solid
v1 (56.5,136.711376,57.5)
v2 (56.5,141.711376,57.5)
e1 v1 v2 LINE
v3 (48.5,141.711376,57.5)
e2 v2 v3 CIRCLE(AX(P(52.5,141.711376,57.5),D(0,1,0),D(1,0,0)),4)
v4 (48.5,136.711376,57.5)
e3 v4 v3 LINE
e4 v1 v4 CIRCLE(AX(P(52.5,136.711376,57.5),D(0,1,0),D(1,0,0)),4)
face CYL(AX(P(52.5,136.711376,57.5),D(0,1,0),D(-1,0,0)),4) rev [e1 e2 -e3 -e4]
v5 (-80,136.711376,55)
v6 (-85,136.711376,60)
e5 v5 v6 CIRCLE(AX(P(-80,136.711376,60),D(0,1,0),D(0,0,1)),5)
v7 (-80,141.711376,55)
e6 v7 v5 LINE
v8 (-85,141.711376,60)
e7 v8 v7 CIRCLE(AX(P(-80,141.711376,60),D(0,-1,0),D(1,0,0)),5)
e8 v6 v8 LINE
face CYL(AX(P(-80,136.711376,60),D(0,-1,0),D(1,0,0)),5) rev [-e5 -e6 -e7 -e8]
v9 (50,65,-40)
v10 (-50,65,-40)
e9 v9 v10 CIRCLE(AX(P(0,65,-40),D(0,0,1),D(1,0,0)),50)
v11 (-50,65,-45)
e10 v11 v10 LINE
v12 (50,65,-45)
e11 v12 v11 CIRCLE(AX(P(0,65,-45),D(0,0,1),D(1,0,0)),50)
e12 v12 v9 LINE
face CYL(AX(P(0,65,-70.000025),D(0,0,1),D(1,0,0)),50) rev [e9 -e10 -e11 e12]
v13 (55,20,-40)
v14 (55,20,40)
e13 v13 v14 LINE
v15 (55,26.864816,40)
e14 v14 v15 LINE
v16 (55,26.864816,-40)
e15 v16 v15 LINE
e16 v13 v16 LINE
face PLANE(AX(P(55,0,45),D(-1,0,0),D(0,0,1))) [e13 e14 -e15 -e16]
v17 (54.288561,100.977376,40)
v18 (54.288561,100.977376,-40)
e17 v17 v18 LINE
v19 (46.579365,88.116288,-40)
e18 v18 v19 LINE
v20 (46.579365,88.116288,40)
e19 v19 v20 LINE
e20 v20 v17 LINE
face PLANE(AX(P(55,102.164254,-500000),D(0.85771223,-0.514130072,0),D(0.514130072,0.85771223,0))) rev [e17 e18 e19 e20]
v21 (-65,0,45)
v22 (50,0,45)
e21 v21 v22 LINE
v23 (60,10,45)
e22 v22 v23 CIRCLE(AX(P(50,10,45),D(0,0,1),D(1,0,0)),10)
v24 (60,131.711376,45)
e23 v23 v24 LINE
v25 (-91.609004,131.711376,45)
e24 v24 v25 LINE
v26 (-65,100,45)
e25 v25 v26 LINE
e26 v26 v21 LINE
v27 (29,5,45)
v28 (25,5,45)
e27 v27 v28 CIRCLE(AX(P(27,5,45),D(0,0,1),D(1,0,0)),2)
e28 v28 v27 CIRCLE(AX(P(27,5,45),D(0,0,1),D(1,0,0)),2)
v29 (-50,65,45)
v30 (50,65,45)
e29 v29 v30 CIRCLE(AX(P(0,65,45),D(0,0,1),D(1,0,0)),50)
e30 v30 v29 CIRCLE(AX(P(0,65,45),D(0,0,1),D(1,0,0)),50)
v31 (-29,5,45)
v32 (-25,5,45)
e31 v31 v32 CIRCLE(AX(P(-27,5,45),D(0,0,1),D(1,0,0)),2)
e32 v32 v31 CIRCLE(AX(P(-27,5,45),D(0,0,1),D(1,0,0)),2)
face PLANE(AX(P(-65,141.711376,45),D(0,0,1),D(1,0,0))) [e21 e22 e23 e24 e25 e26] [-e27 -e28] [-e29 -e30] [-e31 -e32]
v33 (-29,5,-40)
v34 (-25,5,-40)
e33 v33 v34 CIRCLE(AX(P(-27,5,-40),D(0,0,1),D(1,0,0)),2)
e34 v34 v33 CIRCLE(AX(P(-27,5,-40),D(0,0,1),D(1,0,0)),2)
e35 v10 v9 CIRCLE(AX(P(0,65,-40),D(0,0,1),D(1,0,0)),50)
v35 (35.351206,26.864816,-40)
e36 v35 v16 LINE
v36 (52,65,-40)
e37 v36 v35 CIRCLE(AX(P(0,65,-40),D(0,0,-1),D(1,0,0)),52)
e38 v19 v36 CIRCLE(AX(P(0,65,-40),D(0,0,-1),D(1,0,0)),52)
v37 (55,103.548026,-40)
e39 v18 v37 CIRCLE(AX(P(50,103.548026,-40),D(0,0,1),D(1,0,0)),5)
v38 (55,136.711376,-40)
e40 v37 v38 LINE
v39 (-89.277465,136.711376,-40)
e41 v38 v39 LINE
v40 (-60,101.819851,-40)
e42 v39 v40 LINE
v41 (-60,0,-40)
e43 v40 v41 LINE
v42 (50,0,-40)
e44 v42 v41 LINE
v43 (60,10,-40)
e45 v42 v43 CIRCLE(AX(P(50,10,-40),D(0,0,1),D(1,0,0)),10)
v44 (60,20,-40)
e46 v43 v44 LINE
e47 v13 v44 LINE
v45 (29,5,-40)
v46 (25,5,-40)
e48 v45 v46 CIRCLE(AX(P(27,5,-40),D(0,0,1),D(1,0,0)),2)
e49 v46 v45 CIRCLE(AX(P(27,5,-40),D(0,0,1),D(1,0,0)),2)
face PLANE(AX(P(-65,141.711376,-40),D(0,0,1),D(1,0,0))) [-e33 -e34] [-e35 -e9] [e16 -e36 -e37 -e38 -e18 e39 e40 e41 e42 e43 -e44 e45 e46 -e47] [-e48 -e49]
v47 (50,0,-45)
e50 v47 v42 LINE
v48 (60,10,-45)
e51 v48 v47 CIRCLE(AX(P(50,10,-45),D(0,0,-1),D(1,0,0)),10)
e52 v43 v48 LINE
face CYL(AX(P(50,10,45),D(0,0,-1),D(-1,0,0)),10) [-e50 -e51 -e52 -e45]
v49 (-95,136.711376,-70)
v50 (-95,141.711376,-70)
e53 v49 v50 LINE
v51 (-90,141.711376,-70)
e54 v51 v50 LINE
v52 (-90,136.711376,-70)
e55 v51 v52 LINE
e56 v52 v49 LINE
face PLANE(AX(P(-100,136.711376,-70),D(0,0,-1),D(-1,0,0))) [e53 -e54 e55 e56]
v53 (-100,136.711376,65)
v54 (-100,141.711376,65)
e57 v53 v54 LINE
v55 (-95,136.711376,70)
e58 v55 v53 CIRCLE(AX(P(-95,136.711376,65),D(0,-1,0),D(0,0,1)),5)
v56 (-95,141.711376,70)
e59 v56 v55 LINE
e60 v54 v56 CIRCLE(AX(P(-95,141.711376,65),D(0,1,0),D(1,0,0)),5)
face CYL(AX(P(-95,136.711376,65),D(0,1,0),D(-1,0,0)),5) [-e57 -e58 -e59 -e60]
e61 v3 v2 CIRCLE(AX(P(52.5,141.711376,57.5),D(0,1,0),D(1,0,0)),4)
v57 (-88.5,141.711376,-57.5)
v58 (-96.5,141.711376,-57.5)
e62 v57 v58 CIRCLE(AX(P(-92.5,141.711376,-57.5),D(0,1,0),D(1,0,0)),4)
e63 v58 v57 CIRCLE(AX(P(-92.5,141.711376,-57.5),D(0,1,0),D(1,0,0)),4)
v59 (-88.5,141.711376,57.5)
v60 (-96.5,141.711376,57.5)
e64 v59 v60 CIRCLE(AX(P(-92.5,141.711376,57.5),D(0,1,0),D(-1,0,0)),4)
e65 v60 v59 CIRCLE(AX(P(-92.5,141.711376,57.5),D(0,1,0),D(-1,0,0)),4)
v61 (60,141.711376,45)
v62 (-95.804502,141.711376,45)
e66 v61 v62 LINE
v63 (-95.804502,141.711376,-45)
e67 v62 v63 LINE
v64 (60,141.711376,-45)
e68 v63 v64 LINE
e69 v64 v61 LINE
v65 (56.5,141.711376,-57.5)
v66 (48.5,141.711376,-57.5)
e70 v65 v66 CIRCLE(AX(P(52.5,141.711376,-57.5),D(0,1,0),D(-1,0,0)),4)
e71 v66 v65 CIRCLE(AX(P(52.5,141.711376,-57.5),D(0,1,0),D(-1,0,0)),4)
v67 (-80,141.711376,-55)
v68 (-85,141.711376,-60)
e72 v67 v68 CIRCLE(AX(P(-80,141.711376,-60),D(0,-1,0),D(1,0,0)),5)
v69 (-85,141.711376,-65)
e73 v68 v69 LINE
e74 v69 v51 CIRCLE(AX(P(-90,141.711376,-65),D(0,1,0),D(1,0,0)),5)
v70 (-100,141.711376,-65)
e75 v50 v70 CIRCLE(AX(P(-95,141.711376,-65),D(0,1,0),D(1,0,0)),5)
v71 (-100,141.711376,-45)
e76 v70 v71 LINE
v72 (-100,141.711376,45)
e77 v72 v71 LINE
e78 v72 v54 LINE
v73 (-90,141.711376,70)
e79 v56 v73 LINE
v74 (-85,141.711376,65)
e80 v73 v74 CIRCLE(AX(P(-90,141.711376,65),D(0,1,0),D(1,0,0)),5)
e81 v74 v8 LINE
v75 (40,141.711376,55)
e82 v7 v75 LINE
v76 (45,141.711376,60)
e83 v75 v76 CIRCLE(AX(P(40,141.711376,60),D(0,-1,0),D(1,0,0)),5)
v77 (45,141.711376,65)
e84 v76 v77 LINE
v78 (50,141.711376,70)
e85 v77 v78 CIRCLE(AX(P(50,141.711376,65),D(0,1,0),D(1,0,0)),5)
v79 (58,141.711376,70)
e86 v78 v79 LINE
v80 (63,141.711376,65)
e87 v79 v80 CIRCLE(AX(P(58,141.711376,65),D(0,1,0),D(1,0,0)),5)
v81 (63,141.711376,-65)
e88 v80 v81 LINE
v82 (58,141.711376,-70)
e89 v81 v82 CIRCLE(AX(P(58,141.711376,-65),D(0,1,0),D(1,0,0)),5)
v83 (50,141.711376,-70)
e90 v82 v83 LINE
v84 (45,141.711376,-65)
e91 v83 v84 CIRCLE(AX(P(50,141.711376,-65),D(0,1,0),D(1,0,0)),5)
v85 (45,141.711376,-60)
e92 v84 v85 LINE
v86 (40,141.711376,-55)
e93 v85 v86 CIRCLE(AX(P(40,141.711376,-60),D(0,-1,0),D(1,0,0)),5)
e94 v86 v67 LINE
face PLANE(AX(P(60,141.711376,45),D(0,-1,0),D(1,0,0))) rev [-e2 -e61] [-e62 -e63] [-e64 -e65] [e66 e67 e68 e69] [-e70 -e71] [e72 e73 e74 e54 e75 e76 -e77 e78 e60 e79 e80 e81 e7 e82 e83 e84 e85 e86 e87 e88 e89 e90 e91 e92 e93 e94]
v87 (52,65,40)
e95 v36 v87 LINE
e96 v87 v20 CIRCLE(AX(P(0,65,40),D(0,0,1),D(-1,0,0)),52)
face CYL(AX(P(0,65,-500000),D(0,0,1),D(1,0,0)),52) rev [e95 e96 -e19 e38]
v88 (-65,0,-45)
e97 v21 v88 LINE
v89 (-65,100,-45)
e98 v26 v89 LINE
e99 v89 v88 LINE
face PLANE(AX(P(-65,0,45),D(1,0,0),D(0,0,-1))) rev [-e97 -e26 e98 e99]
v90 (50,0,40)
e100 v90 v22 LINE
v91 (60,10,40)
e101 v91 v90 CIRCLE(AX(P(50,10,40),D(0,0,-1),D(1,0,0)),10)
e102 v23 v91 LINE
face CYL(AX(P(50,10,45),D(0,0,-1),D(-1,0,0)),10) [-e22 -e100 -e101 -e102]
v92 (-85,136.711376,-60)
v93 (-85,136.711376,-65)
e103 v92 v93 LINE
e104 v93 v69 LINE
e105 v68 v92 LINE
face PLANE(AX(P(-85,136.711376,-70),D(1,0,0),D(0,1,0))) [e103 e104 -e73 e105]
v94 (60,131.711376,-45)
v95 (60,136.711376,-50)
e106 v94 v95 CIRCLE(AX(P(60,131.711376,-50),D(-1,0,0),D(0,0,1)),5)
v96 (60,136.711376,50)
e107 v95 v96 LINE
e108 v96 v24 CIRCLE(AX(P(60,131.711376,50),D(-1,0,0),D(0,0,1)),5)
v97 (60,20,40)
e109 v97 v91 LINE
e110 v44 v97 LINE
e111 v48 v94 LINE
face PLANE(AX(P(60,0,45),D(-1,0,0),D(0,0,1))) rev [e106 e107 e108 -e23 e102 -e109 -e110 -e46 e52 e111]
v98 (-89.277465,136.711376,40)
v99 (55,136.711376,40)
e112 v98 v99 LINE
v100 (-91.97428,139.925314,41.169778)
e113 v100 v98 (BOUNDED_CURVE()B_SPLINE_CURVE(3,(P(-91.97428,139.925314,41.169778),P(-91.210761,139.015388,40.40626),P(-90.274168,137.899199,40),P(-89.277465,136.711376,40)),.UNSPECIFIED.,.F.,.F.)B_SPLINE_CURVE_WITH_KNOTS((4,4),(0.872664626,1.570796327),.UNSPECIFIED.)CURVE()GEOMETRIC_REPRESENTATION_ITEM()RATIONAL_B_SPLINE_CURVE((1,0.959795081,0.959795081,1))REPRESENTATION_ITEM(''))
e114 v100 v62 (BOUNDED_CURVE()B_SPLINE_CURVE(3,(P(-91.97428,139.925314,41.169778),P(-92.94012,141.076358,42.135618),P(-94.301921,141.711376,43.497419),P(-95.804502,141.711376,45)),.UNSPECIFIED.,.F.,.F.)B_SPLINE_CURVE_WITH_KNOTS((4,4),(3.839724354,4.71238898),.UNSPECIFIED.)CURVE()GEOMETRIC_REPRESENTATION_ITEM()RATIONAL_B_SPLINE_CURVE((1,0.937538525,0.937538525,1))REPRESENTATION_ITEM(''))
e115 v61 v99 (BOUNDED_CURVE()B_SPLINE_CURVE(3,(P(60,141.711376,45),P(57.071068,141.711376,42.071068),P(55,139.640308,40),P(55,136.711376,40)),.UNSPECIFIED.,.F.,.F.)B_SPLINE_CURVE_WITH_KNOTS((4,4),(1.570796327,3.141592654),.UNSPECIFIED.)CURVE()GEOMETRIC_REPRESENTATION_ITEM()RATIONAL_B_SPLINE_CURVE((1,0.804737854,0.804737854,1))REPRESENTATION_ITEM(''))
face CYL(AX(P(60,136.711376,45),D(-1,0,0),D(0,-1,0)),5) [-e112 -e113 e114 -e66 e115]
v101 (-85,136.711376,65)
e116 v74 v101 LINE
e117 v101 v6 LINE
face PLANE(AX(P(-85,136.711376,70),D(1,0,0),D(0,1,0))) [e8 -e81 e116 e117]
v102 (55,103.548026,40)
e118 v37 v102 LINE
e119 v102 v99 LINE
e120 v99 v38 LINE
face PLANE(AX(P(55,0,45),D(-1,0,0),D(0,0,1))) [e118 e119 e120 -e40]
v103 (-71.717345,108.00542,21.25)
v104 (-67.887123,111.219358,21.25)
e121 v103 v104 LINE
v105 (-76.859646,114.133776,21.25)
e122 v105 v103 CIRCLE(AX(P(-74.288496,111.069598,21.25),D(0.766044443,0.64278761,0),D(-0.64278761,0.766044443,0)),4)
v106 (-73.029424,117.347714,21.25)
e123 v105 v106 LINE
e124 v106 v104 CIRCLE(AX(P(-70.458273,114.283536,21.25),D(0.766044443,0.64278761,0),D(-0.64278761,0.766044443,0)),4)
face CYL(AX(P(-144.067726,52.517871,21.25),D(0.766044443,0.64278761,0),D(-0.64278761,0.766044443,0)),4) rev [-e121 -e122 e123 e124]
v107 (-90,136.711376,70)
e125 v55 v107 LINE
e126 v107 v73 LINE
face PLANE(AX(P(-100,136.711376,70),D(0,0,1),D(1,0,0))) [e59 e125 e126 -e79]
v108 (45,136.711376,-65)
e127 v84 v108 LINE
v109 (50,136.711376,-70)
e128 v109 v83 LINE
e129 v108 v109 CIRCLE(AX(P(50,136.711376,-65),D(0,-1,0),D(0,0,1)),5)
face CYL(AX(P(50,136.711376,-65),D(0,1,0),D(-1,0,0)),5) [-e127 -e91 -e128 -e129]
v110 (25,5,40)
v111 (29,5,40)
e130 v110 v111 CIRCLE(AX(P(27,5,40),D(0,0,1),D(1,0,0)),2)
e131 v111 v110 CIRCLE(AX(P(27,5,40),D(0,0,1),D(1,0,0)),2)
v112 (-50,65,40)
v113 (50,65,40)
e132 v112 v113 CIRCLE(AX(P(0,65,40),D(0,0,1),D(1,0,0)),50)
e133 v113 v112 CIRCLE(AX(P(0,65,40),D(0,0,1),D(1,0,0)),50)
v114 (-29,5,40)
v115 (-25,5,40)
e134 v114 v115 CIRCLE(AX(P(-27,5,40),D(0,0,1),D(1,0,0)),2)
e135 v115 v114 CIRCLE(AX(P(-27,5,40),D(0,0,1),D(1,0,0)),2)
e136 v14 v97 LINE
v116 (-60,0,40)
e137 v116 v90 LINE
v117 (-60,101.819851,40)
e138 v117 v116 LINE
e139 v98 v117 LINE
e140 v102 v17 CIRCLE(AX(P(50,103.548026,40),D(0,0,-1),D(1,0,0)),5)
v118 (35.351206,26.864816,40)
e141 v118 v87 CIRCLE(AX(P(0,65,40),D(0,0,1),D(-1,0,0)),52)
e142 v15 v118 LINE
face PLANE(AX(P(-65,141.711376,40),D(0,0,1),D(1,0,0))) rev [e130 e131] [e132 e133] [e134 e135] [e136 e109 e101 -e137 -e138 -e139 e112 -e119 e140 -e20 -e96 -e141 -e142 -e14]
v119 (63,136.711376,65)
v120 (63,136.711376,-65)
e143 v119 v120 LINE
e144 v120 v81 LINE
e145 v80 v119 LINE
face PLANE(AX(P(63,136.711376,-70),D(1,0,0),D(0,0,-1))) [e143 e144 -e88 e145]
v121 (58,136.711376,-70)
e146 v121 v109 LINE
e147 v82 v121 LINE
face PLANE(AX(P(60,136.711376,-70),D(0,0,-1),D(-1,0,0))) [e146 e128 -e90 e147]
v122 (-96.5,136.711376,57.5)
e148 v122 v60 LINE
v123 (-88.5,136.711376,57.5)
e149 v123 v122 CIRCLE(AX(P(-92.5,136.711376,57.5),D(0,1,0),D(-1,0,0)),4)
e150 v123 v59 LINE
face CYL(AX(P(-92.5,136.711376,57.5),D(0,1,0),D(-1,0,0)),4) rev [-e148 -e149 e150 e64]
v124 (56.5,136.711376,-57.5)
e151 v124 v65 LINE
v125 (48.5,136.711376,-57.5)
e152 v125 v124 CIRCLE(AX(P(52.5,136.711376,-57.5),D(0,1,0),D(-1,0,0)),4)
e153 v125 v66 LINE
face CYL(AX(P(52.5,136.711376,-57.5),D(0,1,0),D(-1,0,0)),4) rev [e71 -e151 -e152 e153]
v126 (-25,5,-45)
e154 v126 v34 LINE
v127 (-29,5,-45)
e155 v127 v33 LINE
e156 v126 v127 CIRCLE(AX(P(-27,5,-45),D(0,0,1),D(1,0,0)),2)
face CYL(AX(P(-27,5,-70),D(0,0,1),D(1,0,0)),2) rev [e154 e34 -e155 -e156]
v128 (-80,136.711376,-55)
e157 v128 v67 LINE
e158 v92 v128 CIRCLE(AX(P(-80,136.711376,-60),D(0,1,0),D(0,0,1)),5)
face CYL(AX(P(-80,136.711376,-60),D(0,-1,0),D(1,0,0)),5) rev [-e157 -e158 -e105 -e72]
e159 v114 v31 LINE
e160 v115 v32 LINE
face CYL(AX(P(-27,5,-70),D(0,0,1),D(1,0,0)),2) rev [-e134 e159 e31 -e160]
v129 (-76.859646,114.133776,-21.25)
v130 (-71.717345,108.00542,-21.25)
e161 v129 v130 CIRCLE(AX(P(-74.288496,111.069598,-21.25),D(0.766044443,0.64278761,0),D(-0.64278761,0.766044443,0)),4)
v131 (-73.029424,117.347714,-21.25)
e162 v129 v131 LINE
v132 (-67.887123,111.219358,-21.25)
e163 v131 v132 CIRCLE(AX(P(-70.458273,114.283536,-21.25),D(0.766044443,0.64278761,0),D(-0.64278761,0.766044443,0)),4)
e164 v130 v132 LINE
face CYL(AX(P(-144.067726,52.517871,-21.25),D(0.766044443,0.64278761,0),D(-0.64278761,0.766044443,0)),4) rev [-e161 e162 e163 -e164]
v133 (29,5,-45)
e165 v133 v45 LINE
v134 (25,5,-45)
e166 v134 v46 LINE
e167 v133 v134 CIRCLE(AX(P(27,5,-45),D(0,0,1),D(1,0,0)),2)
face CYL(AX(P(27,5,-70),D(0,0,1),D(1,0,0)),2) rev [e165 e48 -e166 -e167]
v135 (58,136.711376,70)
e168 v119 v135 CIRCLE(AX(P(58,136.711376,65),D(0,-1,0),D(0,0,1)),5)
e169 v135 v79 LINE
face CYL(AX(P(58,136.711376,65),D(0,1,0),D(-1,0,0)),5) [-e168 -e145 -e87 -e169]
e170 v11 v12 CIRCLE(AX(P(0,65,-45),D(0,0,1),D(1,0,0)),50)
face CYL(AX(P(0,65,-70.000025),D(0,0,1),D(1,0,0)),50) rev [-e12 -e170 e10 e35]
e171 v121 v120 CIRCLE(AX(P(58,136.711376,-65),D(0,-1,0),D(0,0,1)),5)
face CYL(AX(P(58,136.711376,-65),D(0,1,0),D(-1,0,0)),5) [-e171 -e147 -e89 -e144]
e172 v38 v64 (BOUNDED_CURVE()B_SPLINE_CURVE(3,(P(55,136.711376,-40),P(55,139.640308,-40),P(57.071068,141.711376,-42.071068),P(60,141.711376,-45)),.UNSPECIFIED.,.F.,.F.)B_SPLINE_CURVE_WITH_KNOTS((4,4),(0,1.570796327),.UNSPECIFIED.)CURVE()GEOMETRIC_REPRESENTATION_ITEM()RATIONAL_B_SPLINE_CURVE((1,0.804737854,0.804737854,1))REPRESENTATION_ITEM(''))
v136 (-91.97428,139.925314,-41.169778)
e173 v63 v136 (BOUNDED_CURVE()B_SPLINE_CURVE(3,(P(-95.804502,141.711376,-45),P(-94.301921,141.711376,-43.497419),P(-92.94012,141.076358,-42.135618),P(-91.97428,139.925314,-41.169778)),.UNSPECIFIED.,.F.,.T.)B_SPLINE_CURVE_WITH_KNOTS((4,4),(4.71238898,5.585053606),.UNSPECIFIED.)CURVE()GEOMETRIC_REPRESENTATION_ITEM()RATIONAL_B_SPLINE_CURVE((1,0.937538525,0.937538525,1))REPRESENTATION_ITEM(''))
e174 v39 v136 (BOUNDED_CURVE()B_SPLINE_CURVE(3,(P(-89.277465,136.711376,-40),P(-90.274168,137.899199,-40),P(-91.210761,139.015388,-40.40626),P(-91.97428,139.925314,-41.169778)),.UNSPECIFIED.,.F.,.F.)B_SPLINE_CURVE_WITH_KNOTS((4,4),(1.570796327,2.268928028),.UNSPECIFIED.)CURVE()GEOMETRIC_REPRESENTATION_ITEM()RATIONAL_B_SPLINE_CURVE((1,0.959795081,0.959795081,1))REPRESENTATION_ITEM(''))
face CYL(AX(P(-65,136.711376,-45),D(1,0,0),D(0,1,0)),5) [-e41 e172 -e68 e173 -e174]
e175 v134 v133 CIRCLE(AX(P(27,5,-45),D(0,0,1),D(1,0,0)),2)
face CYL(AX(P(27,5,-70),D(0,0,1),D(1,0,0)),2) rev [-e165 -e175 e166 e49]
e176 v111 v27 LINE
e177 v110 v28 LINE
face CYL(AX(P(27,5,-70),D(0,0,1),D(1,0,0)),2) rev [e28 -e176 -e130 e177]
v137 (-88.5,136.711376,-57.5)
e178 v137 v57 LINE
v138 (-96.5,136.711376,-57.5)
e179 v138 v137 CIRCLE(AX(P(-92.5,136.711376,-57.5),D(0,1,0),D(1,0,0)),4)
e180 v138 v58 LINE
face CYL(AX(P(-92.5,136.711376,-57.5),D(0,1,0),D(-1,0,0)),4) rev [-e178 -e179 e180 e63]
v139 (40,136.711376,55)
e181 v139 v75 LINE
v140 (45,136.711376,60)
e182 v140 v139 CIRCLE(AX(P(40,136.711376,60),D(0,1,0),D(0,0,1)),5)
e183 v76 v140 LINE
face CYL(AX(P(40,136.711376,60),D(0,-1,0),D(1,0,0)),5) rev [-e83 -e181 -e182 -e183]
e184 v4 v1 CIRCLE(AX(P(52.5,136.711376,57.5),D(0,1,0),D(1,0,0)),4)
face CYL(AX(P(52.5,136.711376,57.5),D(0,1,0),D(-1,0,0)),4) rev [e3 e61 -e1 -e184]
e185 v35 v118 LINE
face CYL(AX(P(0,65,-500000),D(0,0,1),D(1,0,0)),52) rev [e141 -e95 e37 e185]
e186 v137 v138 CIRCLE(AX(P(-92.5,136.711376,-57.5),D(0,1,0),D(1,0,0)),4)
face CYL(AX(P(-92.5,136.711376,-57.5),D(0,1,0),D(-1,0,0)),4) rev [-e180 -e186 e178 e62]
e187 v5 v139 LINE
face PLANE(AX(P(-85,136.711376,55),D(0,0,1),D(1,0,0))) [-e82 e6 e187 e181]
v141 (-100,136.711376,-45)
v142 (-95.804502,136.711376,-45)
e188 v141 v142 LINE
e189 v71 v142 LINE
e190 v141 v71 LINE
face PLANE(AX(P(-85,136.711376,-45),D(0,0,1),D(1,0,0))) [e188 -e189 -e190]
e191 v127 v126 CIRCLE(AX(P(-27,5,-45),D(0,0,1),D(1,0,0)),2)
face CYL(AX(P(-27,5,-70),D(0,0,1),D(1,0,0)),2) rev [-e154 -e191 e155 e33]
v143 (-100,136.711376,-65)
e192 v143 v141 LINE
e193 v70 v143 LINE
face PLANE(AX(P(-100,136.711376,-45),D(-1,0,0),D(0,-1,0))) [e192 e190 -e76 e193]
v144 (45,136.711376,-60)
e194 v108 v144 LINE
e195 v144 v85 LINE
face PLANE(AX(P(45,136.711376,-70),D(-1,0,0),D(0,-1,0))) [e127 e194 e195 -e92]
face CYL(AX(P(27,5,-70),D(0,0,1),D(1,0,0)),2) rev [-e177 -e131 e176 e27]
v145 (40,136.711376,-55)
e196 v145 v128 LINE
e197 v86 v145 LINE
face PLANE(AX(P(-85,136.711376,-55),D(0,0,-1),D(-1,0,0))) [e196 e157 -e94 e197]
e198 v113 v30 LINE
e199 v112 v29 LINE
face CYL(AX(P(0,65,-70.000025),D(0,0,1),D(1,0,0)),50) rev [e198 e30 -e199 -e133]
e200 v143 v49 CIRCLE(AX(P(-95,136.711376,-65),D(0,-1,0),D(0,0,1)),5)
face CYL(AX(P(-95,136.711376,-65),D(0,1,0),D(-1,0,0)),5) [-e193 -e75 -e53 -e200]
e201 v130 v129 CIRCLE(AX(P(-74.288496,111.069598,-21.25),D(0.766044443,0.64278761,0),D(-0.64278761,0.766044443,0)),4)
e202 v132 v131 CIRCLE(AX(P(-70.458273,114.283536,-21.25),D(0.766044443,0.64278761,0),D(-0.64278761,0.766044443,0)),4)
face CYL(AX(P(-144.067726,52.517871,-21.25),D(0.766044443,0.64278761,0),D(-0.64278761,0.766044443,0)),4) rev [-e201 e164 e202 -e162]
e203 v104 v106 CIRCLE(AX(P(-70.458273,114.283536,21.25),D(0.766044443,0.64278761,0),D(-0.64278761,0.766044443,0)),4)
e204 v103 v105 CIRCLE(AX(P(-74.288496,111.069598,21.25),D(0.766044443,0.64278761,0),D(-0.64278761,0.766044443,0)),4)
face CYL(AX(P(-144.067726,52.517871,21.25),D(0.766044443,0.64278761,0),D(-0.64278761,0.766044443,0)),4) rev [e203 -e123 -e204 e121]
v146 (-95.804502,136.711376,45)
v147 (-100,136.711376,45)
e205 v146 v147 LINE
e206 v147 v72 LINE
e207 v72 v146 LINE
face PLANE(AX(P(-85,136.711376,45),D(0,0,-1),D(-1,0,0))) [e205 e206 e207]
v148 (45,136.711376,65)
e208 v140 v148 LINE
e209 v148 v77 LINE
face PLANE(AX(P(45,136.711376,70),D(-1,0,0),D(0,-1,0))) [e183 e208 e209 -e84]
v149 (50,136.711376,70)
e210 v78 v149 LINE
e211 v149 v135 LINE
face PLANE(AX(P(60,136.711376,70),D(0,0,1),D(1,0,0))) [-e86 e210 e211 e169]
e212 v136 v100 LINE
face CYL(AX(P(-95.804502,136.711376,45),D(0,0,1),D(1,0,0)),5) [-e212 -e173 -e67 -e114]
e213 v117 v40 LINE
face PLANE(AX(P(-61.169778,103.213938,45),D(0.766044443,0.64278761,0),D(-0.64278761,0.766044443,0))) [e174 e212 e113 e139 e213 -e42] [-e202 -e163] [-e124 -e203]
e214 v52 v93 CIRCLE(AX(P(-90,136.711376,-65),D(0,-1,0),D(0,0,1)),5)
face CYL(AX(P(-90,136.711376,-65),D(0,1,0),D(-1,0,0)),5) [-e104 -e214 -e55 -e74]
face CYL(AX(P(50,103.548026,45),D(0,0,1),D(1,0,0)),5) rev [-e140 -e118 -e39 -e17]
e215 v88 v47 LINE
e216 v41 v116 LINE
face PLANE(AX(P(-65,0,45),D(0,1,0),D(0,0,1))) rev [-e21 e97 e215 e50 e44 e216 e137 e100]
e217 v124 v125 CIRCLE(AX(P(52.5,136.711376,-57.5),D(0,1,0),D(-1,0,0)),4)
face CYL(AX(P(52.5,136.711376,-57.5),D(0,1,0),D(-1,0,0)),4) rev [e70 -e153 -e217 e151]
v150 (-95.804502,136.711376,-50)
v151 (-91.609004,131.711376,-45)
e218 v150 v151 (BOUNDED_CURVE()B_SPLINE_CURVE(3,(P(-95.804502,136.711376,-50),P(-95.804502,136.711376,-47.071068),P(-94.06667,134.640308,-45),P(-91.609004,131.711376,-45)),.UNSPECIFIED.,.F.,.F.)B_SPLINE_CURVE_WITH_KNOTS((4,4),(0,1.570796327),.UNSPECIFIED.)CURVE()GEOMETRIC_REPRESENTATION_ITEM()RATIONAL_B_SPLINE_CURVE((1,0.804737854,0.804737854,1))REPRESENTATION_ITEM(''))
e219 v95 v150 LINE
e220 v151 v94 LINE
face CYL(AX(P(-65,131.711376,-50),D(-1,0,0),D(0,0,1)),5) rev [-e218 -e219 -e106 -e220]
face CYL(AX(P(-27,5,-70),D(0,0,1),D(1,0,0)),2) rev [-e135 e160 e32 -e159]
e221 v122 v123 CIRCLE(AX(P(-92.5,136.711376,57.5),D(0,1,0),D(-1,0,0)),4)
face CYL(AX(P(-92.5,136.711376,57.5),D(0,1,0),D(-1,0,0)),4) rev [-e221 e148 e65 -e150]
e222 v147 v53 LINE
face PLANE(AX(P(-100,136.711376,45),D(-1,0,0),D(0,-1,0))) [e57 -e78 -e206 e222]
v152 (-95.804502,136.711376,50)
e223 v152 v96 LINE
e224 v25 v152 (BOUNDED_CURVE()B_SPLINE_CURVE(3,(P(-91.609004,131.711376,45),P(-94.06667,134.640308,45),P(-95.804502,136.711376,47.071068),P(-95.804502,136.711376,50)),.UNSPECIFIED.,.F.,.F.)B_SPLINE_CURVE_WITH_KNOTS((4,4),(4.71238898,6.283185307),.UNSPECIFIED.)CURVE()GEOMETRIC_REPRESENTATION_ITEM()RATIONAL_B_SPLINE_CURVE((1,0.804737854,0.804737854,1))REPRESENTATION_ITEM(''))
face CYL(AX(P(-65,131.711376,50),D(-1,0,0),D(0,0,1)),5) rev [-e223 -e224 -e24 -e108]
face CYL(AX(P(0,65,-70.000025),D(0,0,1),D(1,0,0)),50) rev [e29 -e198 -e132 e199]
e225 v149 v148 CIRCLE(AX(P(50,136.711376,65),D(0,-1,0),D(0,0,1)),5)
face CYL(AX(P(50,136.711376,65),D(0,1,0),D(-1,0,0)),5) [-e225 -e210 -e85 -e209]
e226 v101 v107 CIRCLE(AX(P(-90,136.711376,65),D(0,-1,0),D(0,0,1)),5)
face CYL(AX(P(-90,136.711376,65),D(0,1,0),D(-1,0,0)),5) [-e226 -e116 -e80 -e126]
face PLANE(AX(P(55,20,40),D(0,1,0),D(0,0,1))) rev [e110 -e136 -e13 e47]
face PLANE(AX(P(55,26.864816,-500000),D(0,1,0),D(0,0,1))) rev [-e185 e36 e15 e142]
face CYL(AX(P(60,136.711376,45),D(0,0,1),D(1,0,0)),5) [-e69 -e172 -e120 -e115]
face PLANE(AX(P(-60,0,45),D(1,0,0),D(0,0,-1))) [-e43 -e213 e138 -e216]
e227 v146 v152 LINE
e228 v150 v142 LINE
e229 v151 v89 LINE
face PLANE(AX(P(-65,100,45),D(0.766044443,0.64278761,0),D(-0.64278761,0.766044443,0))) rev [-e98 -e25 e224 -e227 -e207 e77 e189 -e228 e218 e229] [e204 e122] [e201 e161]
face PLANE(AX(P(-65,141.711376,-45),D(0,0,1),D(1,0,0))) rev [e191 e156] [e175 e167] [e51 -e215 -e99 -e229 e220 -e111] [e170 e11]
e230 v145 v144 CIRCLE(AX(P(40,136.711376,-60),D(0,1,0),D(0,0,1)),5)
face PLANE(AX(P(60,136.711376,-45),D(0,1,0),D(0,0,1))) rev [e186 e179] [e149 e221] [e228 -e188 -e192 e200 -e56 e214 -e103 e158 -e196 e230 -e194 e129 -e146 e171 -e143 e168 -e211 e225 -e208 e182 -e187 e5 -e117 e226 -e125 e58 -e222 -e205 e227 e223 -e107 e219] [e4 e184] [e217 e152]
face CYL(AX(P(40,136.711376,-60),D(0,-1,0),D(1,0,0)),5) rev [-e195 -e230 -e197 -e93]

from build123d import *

# Parameters (mm, degrees)
EXTRUDE_1_DEPTH      = 45
SHELL_1_T            = -5
SKETCH_2_W           = 15
SKETCH_2_H           = 25
SKETCH_2_R           = 4
EXTRUDE_2_DEPTH      = 5
SKETCH_3_W           = 115
SKETCH_3_H           = 80
CUT_EXTRUDE_3_DEPTH  = 184.275749233
SKETCH_4_W           = 80
SKETCH_4_H           = 20
CUT_EXTRUDE_4_DEPTH  = 5
SKETCH_5_R           = 50
CUT_EXTRUDE_5_DEPTH  = 209.10361365
EXTRUDE_6_REACH      = 207.383
SKETCH_7_W           = 130
SKETCH_7_H           = 10
SKETCH_7_W_2         = 3
SKETCH_7_H_2         = 140
EXTRUDE_7_DEPTH      = 5
FILLET_1_R           = 5
FILLET_2_R           = 5
FILLET_3_R           = 5
FILLET_4_R           = 5
FILLET_5_R           = 5
FILLET_6_R           = 10
SKETCH_15_R          = 4
CUT_EXTRUDE_16_DEPTH = 187.54027319
SKETCH_16_R          = 2
CUT_EXTRUDE_17_DEPTH = 209.10361365


with BuildPart() as part:
    # 草图1 → 拉伸1 (new, symmetric)
    with BuildSketch(Plane.XY):
        Polygon((-65, 0), (60, 0), (60, 141.711375741), (-100, 141.711375741), (-65, 100), align=None)
    extrude(amount=EXTRUDE_1_DEPTH, both=True)

    # 抽壳1
    shell_1_openings = [part.faces().sort_by_distance(p)[0] for p in [
        (-20, 141.711375741, 0),
    ]]
    offset(amount=SHELL_1_T, openings=shell_1_openings, kind=Kind.INTERSECTION)

    # 草图2 → 拉伸2 (add)
    # profile 1 of 4: a face of its own
    with BuildSketch(Plane(origin=(0, 141.711375741, 0), x_dir=(1, 0, 0), z_dir=(0, 1, 0))):
        with Locations((52.5, 57.5)):
            Rectangle(SKETCH_2_W, SKETCH_2_H)
        with Locations(Location((52.5, 57.5, 0), (0, 0, 180))):
            Circle(SKETCH_2_R, mode=Mode.SUBTRACT)
    # profile 2 of 4: a face of its own
    with BuildSketch(Plane(origin=(0, 141.711375741, 0), x_dir=(1, 0, 0), z_dir=(0, 1, 0))):
        with Locations((-92.5, -57.5)):
            Rectangle(SKETCH_2_W, SKETCH_2_H)
        with Locations(Location((-92.5, -57.5, 0), (0, 0, 180))):
            Circle(SKETCH_2_R, mode=Mode.SUBTRACT)
    # profile 3 of 4: a face of its own
    with BuildSketch(Plane(origin=(0, 141.711375741, 0), x_dir=(1, 0, 0), z_dir=(0, 1, 0))):
        with Locations((52.5, -57.5)):
            Rectangle(SKETCH_2_W, SKETCH_2_H)
        with Locations((52.5, -57.5)):
            Circle(SKETCH_2_R, mode=Mode.SUBTRACT)
    # profile 4 of 4: a face of its own
    with BuildSketch(Plane(origin=(0, 141.711375741, 0), x_dir=(1, 0, 0), z_dir=(0, 1, 0))):
        with Locations((-92.5, 57.5)):
            Rectangle(SKETCH_2_W, SKETCH_2_H)
        with Locations((-92.5, 57.5)):
            Circle(SKETCH_2_R, mode=Mode.SUBTRACT)
    extrude(amount=-EXTRUDE_2_DEPTH)

    # 草图3 → 拉伸3 (cut, through all)
    with BuildSketch(Plane(origin=(0, 5, 0), x_dir=(1, 0, 0), z_dir=(0, 1, 0))):
        with Locations((-2.5, 0)):
            Rectangle(SKETCH_3_W, SKETCH_3_H)
    extrude(amount=-CUT_EXTRUDE_3_DEPTH, mode=Mode.SUBTRACT)

    # 草图4 → 拉伸4 (cut)
    with BuildSketch(Plane(origin=(60, 0, 0), x_dir=(0, 0, -1), z_dir=(1, 0, 0))):
        with Locations((0, 10)):
            Rectangle(SKETCH_4_W, SKETCH_4_H)
    extrude(amount=-CUT_EXTRUDE_4_DEPTH, mode=Mode.SUBTRACT)

    # 草图5 → 拉伸5 (cut, through all)
    with BuildSketch(Plane.XY.offset(45)):
        with Locations((0, 65)):
            Circle(SKETCH_5_R)
    extrude(amount=-CUT_EXTRUDE_5_DEPTH, mode=Mode.SUBTRACT)

    # 草图6 → 拉伸6 (add, up to next)
    with BuildSketch(Plane(origin=(0, 0, 40), x_dir=(-1, 0, 0), z_dir=(0, 0, -1)), mode=Mode.PRIVATE) as extrude_6_sk1:
        with BuildLine():
            Line((-55, 102.164254348), (-46.579364738, 88.116288209))
            ThreePointArc((-46.579364738, 88.116288209), (-51.147730221, 55.623983082), (-35.351205937, 26.864816261))
            Line((-35.351205937, 26.864816261), (-55, 26.864816261))
            Line((-55, 26.864816261), (-55, 102.164254348))
        make_face()
    extrude_6_tool1 = extrude(extrude_6_sk1.sketch, amount=EXTRUDE_6_REACH, mode=Mode.PRIVATE) - part.part
    add(extrude_6_tool1.solids().sort_by_distance((45.175603, 27.643024, 40))[0])

    # 草图7 → 拉伸7 (add)
    with BuildSketch(Plane(origin=(0, 141.711375741, 0), x_dir=(1, 0, 0), z_dir=(0, 1, 0))):
        with Locations((-20, 50)):
            Rectangle(SKETCH_7_W, SKETCH_7_H)
        with Locations((-20, -50)):
            Rectangle(SKETCH_7_W, SKETCH_7_H)
        with Locations((61.5, 0)):
            Rectangle(SKETCH_7_W_2, SKETCH_7_H_2)
    extrude(amount=-EXTRUDE_7_DEPTH)

    # 圆角1
    fillet_1_edges = [part.edges().sort_by_distance(p)[0] for p in [
        (-19.236481777, 141.711375741, -40),
        (-19.236481777, 141.711375741, 40),
    ]]
    fillet(fillet_1_edges, radius=FILLET_1_R)

    # 圆角2
    fillet_2_edges = [part.edges().sort_by_distance(p)[0] for p in [
        (55, 141.711375741, 0),
        (-93.472963553, 141.711375741, 0),
    ]]
    fillet(fillet_2_edges, radius=FILLET_2_R)

    # 圆角3
    fillet_3_edges = [part.edges().sort_by_distance(p)[0] for p in [
        (55, 102.164254348, 0),
    ]]
    fillet(fillet_3_edges, radius=FILLET_3_R)

    # 圆角4
    fillet_4_edges = [part.edges().sort_by_distance(p)[0] for p in [
        (45, 139.211375741, -55),
        (45, 139.211375741, -70),
        (63, 139.211375741, -70),
        (63, 139.211375741, 70),
        (45, 139.211375741, 55),
        (45, 139.211375741, 70),
        (-100, 139.211375741, -70),
        (-85, 139.211375741, -70),
        (-85, 139.211375741, -55),
        (-100, 139.211375741, 70),
        (-85, 139.211375741, 70),
        (-85, 139.211375741, 55),
    ]]
    fillet(fillet_4_edges, radius=FILLET_4_R)

    # 圆角5
    fillet_5_edges = [part.edges().sort_by_distance(p)[0] for p in [
        (-17.902250922, 136.711375741, -45),
        (-17.902250922, 136.711375741, 45),
    ]]
    fillet(fillet_5_edges, radius=FILLET_5_R)

    # 圆角6
    fillet_6_edges = [part.edges().sort_by_distance(p)[0] for p in [
        (60, 0, 42.5),
        (60, 0, -42.5),
    ]]
    fillet(fillet_6_edges, radius=FILLET_6_R)

    # 草图15 → 拉伸16 (cut, through all)
    with BuildSketch(Plane(origin=(14.927044092, 12.525277192, 0), x_dir=(0.6427876096865403, -0.7660444431189775, 0), z_dir=(0.7660444431189775, 0.6427876096865403, 0))):
        with Locations(Location((-132.835972882, -21.25, 0), (0, 0, 180))):
            Circle(SKETCH_15_R)
        with Locations(Location((-132.835972882, 21.25, 0), (0, 0, 180))):
            Circle(SKETCH_15_R)
    extrude(amount=-CUT_EXTRUDE_16_DEPTH, mode=Mode.SUBTRACT)

    # 草图16 → 拉伸17 (cut, through all)
    with BuildSketch(Plane.XY.offset(45)):
        with Locations((-27, 5)):
            Circle(SKETCH_16_R)
        with Locations((27, 5)):
            Circle(SKETCH_16_R)
    extrude(amount=-CUT_EXTRUDE_17_DEPTH, mode=Mode.SUBTRACT)


solid = part.part
